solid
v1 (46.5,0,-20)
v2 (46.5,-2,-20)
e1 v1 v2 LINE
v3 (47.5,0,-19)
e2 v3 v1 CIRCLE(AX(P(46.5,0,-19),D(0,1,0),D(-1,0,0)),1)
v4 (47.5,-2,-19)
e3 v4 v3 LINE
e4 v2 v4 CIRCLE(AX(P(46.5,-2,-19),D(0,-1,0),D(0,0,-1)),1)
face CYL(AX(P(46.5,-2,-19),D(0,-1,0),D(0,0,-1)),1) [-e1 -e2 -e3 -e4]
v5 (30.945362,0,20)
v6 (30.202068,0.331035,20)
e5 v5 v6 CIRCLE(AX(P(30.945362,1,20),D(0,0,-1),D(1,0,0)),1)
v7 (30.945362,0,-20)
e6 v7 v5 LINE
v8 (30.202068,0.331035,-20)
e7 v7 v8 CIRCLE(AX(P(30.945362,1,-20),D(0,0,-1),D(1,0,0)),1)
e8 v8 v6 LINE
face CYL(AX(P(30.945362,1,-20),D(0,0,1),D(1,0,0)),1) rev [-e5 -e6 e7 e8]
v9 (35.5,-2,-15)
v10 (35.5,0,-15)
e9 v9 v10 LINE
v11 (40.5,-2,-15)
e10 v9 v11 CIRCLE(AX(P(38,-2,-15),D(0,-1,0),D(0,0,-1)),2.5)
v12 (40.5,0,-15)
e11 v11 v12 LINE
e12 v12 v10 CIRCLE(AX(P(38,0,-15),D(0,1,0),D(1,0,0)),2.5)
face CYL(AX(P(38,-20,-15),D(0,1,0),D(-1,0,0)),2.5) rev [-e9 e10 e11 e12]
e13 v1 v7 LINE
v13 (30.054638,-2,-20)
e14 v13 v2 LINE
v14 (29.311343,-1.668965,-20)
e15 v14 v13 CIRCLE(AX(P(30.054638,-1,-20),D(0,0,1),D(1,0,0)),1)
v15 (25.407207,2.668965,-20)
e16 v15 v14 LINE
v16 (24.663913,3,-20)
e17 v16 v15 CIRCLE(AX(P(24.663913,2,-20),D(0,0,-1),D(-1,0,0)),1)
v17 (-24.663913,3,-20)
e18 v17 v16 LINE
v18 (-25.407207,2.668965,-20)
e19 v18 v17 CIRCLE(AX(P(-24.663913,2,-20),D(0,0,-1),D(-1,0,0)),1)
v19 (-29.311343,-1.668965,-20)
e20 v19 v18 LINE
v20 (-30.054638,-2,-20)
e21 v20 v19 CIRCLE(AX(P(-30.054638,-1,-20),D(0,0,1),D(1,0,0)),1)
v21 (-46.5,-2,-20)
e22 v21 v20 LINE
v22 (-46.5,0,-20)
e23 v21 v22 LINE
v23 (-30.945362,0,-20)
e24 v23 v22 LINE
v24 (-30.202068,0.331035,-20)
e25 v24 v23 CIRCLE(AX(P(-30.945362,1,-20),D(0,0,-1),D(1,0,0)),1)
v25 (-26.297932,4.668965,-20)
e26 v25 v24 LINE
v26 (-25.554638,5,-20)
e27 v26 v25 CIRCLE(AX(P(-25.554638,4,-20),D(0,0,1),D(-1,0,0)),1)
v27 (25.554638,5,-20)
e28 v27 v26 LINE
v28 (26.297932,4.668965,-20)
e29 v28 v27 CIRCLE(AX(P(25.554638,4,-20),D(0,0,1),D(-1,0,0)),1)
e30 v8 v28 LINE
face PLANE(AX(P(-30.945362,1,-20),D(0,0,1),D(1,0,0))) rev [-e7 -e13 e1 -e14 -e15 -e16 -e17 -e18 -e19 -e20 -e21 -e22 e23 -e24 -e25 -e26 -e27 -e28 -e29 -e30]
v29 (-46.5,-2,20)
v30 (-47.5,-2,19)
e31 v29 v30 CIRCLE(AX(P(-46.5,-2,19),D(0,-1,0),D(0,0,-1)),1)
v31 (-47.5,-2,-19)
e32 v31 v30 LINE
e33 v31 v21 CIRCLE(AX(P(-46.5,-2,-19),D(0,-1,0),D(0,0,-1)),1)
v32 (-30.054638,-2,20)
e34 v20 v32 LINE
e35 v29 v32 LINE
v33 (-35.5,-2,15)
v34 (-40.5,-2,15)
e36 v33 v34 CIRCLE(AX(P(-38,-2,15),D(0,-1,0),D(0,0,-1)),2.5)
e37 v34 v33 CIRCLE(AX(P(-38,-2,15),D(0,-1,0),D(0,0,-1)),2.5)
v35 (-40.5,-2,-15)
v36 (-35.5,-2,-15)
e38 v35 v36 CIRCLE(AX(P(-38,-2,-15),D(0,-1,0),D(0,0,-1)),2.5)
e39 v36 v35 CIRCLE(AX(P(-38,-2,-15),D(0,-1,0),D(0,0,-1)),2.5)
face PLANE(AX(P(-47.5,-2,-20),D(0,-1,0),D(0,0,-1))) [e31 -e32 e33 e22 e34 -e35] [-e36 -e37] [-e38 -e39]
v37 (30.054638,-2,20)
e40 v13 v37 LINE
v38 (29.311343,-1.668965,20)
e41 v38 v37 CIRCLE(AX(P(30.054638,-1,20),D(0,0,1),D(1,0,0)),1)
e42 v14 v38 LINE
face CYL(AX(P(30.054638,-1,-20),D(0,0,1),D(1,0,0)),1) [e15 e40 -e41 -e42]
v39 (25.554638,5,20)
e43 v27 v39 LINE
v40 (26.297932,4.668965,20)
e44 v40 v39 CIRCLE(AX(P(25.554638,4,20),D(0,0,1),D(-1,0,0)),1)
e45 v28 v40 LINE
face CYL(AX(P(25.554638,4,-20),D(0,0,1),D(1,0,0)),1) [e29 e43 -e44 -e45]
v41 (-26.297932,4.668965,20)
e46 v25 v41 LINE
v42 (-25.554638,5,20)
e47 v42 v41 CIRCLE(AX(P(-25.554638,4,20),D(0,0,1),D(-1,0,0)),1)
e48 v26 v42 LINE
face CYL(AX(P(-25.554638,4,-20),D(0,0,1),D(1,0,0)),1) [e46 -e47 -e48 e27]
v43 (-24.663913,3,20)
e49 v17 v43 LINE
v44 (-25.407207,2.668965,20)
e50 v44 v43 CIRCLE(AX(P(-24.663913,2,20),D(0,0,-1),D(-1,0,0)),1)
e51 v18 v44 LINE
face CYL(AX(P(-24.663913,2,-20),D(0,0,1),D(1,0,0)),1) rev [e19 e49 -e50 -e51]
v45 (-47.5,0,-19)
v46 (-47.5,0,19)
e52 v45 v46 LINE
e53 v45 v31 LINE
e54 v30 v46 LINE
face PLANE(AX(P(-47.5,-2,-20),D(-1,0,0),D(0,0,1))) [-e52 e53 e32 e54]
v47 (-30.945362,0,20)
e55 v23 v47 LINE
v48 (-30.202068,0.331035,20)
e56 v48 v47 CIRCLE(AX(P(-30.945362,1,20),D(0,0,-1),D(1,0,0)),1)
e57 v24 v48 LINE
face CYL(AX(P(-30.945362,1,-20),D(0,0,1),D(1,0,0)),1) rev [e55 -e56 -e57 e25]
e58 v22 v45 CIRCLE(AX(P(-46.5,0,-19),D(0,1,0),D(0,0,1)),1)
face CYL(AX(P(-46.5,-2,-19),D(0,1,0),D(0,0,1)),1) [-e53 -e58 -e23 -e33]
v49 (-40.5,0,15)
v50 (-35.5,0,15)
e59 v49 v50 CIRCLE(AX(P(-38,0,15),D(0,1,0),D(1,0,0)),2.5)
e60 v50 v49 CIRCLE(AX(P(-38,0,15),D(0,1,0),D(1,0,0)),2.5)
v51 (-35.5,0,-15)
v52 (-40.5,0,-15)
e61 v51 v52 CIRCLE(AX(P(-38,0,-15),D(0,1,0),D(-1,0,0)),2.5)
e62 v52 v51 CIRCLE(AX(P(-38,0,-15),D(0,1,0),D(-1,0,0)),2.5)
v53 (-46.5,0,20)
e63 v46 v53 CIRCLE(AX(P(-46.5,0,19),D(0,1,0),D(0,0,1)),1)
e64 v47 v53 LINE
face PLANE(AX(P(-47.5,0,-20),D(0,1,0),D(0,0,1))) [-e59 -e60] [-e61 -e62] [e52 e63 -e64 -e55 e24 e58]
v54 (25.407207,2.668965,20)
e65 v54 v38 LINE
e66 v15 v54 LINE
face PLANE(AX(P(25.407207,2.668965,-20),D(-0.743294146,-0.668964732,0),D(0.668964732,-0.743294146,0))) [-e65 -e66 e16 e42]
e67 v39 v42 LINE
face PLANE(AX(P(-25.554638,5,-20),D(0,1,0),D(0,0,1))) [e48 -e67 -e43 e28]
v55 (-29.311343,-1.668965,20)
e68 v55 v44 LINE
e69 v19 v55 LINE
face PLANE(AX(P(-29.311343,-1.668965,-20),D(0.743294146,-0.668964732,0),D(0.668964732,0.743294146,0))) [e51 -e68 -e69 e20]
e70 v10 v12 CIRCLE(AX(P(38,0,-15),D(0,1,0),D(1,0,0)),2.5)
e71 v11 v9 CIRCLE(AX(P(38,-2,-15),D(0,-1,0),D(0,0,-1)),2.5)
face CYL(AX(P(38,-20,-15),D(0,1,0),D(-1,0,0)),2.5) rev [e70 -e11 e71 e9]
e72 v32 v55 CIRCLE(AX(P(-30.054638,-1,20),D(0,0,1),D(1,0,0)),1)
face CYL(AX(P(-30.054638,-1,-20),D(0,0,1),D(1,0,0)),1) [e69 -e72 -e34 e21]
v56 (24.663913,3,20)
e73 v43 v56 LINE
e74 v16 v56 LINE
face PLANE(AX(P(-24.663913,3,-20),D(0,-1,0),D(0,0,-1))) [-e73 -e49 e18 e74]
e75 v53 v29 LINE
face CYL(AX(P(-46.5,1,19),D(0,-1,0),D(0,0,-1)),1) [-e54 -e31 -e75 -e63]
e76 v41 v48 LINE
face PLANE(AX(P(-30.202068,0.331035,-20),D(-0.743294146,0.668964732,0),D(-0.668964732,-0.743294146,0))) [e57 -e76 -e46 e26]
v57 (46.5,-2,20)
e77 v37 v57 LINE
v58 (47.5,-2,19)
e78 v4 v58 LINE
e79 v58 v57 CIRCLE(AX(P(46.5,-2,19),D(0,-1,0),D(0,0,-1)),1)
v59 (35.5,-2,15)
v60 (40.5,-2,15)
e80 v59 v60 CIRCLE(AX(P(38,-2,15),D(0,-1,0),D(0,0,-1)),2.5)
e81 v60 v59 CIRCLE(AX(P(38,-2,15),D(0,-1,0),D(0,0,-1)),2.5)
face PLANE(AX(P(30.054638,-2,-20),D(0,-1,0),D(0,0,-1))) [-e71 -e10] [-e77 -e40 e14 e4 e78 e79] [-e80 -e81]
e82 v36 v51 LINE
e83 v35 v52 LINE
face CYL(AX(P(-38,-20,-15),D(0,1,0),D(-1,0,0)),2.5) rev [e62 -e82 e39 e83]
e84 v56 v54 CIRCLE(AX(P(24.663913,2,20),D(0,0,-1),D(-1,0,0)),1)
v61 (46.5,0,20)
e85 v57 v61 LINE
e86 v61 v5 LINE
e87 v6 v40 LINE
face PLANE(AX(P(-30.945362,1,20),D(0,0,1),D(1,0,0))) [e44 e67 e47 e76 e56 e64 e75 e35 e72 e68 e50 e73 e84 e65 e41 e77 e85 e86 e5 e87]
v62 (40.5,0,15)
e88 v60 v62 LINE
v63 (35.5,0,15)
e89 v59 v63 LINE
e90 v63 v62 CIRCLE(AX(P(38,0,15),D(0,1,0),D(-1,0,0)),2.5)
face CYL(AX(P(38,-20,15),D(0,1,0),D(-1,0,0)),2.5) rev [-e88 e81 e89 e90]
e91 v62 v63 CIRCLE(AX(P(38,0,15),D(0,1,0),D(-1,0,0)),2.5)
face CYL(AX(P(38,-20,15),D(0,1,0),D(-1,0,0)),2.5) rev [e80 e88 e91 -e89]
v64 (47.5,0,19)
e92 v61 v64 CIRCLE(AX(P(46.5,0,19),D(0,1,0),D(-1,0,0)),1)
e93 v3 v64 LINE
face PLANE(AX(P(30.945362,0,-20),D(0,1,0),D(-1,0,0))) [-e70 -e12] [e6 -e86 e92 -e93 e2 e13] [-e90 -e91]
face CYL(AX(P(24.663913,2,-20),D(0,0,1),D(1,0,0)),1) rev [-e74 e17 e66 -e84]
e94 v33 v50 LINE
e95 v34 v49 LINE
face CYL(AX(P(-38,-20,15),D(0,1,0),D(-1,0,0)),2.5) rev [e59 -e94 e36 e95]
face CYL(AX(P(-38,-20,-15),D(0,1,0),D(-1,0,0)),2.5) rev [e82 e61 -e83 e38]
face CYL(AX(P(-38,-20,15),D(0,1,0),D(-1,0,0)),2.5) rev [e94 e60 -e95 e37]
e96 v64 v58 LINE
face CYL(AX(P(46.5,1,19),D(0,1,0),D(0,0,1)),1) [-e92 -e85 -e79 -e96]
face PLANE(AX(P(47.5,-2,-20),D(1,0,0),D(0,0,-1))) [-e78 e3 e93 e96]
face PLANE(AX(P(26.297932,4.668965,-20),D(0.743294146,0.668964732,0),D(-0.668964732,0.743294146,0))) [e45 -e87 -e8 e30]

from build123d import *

# Parameters (mm, degrees)
BOSS_EXTRUDE1_DEPTH      = 20
BOSS_EXTRUDE1_DEPTH_BACK = 20
SKETCH2_R                = 2.5
CUT_EXTRUDE1_DEPTH       = 20
FILLET1_R                = 1


with BuildPart() as part:
    # Sketch1 → Boss-Extrude1 (new, two sides: drawn at the far end of the back side and taken through both)
    with BuildSketch(Plane.XY.offset(-BOSS_EXTRUDE1_DEPTH_BACK)):
        with BuildLine():
            Line((-47.5, 0), (-30.945362405, 0))
            ThreePointArc((-30.945362405, 0), (-30.53852382, 0.086499937), (-30.202068258, 0.331035268))
            Line((-30.202068258, 0.331035268), (-26.297931742, 4.668964732))
            ThreePointArc((-26.297931742, 4.668964732), (-25.96147618, 4.913500063), (-25.554637595, 5))
            Line((-25.554637595, 5), (25.554637595, 5))
            ThreePointArc((25.554637595, 5), (25.96147618, 4.913500063), (26.297931742, 4.668964732))
            Line((26.297931742, 4.668964732), (30.202068258, 0.331035268))
            ThreePointArc((30.202068258, 0.331035268), (30.53852382, 0.086499937), (30.945362405, 0))
            Line((30.945362405, 0), (47.5, 0))
            Line((47.5, 0), (47.5, -2))
            Line((47.5, -2), (30.054637595, -2))
            ThreePointArc((30.054637595, -2), (29.64779901, -1.913500063), (29.311343449, -1.668964732))
            Line((29.311343449, -1.668964732), (25.407206932, 2.668964732))
            ThreePointArc((25.407206932, 2.668964732), (25.070751371, 2.913500063), (24.663912786, 3))
            Line((24.663912786, 3), (-24.663912786, 3))
            ThreePointArc((-24.663912786, 3), (-25.070751371, 2.913500063), (-25.407206932, 2.668964732))
            Line((-25.407206932, 2.668964732), (-29.311343449, -1.668964732))
            ThreePointArc((-29.311343449, -1.668964732), (-29.64779901, -1.913500063), (-30.054637595, -2))
            Line((-30.054637595, -2), (-47.5, -2))
            Line((-47.5, -2), (-47.5, 0))
        make_face()
    extrude(amount=BOSS_EXTRUDE1_DEPTH + BOSS_EXTRUDE1_DEPTH_BACK)

    # Sketch2 → Cut-Extrude1 (cut)
    with BuildSketch(Plane(origin=(0, 0, 0), x_dir=(1, 0, 0), z_dir=(0, 1, 0))):
        with Locations(Location((-38, 15, 0), (0, 0, 180))):
            Circle(SKETCH2_R)
        with Locations(Location((38, 15, 0), (0, 0, 90))):
            Circle(SKETCH2_R)
        with Locations(Location((38, -15, 0), (0, 0, 180))):
            Circle(SKETCH2_R)
        with Locations(Location((-38, -15, 0), (0, 0, 90))):
            Circle(SKETCH2_R)
    extrude(amount=-CUT_EXTRUDE1_DEPTH, mode=Mode.SUBTRACT)

    # Fillet1
    fillet1_edges = [part.edges().sort_by_distance(p)[0] for p in [
        (47.5, -1, -20),
        (-47.5, -1, -20),
        (-47.5, -1, 20),
        (47.5, -1, 20),
    ]]
    fillet(fillet1_edges, radius=FILLET1_R)


solid = part.part
